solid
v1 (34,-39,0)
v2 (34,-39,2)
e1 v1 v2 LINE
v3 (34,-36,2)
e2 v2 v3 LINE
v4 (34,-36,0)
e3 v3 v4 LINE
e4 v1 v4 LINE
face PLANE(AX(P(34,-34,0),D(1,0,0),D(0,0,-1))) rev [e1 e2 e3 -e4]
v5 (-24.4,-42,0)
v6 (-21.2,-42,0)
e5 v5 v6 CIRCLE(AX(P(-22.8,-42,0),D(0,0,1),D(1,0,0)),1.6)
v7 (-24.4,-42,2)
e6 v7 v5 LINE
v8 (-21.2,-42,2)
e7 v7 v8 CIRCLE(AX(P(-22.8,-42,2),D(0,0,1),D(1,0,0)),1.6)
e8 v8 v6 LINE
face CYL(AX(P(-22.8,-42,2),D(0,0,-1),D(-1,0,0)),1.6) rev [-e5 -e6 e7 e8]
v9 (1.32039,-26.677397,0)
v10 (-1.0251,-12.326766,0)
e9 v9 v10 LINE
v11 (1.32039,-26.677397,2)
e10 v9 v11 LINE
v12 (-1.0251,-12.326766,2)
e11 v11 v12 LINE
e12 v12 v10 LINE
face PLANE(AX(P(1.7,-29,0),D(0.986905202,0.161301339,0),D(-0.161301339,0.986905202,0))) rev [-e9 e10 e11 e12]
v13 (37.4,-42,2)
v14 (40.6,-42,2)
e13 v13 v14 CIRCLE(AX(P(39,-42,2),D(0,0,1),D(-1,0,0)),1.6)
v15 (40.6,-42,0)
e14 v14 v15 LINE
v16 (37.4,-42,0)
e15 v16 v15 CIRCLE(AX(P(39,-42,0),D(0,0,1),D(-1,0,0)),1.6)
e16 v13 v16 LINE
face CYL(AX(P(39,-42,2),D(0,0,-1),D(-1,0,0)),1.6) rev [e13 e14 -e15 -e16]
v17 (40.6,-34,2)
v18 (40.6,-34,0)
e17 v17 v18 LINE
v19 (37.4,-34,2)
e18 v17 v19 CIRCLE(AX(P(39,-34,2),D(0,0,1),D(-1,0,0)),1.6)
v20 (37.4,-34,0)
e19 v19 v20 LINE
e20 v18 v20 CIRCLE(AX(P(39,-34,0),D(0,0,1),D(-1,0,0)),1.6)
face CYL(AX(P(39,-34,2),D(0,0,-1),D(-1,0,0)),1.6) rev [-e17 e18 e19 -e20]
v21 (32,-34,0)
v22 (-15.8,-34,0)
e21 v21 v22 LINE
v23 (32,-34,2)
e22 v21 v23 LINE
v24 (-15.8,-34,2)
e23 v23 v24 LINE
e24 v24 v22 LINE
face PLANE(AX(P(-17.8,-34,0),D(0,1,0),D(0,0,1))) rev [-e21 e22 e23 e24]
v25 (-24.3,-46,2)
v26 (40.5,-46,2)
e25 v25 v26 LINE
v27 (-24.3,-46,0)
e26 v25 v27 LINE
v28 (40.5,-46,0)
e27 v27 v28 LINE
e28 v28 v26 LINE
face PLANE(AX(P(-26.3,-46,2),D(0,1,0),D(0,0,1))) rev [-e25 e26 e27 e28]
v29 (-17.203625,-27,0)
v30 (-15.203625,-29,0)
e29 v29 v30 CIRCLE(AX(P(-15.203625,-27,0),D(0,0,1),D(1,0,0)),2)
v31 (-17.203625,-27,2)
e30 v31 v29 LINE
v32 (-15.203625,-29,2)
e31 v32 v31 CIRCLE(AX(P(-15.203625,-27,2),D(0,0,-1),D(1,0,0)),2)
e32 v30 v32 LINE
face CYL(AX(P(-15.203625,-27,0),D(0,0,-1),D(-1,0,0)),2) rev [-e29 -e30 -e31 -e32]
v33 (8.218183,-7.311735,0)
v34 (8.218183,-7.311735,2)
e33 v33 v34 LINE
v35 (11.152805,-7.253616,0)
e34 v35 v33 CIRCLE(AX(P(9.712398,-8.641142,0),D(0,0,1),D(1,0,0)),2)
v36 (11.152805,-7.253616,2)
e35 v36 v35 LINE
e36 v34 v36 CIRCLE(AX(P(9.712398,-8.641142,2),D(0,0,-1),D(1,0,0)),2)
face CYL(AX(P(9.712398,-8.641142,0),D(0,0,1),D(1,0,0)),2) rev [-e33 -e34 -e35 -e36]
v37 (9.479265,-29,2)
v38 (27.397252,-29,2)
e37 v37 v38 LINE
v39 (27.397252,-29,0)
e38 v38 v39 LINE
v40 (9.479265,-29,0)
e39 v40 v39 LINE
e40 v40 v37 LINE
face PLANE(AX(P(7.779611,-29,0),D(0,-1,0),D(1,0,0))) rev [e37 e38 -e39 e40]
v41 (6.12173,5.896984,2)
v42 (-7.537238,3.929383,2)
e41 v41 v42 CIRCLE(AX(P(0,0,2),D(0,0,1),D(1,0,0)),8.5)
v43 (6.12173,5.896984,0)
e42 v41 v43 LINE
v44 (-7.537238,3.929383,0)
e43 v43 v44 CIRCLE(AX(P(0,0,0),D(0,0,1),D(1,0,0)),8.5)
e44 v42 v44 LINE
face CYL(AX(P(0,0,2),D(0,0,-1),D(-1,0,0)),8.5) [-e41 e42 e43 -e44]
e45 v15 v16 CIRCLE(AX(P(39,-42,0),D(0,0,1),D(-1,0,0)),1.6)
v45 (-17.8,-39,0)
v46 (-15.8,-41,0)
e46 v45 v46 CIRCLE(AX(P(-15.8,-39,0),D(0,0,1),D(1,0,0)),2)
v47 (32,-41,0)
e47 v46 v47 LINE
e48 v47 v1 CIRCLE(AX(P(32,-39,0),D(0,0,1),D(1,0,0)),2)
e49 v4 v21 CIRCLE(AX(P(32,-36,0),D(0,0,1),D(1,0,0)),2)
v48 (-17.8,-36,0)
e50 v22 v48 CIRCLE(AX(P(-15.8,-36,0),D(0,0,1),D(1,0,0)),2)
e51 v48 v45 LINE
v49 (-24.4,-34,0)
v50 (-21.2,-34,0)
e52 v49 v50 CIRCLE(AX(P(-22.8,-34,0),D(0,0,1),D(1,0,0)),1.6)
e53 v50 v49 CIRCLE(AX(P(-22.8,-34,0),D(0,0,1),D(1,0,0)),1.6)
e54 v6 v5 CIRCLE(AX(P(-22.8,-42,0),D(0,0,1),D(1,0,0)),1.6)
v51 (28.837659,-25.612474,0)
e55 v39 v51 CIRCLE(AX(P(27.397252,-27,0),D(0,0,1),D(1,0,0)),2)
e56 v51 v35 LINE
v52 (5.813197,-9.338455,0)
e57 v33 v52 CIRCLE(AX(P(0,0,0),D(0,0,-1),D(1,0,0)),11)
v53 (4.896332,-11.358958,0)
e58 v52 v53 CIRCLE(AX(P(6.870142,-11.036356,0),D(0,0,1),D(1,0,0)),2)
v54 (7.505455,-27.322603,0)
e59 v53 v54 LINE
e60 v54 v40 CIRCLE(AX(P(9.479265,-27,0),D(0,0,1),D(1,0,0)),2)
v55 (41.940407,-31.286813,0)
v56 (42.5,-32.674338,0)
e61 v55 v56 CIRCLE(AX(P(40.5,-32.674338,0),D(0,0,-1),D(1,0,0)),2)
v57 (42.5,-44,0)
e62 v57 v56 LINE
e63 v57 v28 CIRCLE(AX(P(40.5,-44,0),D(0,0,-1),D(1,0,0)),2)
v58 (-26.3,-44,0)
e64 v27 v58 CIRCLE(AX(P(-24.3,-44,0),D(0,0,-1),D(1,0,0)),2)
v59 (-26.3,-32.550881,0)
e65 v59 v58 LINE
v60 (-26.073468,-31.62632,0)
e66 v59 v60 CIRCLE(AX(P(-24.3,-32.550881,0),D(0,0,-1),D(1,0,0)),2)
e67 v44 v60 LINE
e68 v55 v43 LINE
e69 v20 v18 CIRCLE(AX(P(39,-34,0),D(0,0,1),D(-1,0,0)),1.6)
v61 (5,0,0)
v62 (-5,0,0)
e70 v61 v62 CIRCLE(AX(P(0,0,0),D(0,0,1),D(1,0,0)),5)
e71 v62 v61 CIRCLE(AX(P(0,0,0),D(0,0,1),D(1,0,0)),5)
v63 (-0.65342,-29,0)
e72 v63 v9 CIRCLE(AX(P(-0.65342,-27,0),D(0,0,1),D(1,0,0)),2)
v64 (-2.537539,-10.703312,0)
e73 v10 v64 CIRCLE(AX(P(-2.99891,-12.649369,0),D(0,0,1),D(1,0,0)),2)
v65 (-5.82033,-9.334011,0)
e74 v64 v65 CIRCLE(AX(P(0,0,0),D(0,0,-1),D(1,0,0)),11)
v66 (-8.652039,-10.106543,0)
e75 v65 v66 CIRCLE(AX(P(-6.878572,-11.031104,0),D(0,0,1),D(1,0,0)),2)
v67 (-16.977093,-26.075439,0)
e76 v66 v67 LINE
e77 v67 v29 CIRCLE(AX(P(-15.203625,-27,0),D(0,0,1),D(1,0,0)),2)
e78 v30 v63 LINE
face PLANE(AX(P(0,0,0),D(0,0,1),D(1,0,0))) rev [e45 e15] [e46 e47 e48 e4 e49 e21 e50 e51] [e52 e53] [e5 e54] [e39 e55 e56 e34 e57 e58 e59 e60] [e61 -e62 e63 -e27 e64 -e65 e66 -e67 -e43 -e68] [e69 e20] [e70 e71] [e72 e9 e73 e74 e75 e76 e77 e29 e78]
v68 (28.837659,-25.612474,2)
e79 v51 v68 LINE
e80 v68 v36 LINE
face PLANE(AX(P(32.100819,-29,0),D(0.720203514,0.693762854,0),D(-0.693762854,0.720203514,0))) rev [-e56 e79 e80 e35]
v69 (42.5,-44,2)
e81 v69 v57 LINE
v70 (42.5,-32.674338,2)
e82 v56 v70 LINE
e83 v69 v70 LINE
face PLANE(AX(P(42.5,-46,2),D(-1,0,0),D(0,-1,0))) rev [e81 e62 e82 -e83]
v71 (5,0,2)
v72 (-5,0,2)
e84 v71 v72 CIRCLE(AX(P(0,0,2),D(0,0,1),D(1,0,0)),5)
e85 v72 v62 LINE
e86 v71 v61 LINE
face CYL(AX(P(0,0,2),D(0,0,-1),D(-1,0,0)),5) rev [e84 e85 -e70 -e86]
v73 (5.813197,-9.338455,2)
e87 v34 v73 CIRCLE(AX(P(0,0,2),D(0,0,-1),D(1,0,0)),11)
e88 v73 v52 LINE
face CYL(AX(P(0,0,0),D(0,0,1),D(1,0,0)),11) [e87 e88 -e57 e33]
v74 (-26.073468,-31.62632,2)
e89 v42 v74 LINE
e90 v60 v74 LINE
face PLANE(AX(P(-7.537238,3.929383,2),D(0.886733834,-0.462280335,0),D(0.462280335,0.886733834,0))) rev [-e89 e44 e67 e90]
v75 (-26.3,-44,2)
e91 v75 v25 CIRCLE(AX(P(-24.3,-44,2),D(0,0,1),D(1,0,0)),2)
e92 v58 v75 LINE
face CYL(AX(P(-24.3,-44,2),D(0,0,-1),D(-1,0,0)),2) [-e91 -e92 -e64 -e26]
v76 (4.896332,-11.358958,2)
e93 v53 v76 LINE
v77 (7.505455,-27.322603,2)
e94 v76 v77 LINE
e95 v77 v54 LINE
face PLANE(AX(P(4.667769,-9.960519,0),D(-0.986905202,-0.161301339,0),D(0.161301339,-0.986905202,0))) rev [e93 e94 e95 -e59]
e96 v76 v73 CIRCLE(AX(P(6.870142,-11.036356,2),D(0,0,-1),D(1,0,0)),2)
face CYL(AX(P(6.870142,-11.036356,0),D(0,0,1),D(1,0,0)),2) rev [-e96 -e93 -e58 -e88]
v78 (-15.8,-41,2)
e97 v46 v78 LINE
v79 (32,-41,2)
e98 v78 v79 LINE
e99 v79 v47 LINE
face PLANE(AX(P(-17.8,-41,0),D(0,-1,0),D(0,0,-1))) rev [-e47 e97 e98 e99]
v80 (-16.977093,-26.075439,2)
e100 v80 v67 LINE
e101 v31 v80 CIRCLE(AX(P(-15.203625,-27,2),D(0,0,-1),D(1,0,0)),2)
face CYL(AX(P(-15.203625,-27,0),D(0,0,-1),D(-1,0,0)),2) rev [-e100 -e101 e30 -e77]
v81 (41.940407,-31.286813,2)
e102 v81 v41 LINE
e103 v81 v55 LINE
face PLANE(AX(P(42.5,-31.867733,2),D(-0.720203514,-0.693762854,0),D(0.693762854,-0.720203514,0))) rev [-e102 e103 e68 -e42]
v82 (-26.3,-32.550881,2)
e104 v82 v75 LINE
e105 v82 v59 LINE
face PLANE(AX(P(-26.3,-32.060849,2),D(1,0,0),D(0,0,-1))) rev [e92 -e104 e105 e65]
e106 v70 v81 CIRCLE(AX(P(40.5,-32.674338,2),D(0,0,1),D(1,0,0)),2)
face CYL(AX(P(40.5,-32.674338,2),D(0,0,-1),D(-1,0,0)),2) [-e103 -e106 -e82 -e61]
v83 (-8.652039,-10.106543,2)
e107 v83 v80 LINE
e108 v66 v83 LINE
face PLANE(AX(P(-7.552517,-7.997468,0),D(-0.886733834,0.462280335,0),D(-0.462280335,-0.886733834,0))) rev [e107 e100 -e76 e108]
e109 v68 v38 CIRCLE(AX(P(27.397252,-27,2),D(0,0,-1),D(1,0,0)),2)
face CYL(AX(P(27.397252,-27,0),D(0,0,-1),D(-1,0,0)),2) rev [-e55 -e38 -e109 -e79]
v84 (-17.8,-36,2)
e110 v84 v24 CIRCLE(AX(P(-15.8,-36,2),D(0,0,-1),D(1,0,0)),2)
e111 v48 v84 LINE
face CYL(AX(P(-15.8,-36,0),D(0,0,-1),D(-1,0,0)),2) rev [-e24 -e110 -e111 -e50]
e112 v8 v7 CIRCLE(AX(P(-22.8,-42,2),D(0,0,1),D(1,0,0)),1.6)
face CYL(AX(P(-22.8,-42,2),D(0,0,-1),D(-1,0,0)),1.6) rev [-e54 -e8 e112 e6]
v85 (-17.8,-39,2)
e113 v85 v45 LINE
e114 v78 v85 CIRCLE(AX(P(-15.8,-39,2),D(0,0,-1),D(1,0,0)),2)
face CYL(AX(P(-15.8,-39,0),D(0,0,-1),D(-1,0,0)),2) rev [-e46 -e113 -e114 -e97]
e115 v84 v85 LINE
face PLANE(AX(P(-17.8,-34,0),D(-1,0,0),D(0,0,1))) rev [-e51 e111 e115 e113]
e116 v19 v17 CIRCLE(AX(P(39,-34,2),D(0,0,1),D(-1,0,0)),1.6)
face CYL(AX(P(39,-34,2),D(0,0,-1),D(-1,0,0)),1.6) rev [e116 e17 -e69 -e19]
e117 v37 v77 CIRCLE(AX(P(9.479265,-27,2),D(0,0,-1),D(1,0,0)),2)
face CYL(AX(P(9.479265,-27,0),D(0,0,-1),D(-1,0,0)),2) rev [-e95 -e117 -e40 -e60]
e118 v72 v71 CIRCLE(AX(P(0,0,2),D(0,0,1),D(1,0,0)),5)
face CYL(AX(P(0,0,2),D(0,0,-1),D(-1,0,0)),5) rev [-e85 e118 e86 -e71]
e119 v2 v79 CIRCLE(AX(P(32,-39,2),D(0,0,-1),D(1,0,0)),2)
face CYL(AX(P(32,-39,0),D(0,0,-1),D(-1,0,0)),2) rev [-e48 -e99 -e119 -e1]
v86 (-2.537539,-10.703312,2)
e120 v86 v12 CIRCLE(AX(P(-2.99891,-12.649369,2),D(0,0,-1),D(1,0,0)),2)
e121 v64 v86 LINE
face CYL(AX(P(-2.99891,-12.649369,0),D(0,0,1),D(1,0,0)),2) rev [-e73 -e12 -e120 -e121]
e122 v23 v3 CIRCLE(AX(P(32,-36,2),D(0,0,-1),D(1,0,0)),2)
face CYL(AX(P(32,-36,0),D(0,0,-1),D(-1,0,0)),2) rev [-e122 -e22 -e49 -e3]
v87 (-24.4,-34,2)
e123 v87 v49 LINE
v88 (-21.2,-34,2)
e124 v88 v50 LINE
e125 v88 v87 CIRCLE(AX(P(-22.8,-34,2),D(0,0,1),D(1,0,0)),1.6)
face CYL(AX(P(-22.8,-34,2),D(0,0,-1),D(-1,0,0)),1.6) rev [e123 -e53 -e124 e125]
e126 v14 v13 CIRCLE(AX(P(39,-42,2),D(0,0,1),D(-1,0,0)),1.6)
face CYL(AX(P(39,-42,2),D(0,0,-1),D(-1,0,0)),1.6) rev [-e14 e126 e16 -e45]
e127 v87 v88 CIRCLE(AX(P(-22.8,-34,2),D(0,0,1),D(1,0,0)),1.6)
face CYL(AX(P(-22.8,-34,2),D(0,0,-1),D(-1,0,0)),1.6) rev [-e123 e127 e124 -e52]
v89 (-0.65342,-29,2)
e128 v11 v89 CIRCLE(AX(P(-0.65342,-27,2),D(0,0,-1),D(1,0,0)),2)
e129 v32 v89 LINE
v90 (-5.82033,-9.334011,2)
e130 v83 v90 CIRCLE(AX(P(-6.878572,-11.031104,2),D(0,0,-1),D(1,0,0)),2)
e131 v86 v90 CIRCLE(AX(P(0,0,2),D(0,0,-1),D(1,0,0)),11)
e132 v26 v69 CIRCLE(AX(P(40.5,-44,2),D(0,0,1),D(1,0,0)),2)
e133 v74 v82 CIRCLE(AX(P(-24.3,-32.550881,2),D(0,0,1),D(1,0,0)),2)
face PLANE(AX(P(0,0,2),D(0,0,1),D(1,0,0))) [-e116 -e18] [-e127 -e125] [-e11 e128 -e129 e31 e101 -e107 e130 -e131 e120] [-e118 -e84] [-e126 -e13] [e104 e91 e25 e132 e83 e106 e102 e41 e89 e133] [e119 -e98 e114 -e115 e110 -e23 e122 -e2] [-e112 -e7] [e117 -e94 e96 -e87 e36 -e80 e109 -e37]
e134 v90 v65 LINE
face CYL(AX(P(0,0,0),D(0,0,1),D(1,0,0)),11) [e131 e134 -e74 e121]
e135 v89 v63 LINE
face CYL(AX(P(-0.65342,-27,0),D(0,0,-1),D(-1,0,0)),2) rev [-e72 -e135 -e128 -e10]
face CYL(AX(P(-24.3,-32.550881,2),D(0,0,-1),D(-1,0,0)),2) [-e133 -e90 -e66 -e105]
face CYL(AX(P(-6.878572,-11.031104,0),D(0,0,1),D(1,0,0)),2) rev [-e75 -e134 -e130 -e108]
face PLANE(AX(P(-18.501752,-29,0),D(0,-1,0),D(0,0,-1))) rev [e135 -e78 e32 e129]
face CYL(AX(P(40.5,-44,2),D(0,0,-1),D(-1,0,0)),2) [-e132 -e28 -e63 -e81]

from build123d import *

# Parameters (mm, degrees)
SKETCH_1_R          = 5
SKETCH_1_R_2        = 1.6
EXTRUDE_1_DEPTH     = 2
SKETCH_6_W          = 51.8
SKETCH_6_H          = 7
CUT_EXTRUDE_4_DEPTH = 63.659795723
FILLET_5_R          = 2
FILLET_6_R          = 2


with BuildPart() as part:
    # 草图1 → 凸台-拉伸1 (new body)
    with BuildSketch(Plane.XY):
        with BuildLine():
            Line((-26.3, -32.06084855), (-26.3, -46))
            Line((-26.3, -46), (42.5, -46))
            Line((42.5, -46), (42.5, -31.867732913))
            Line((42.5, -31.867732913), (6.12172987, 5.896984263))
            ThreePointArc((6.12172987, 5.896984263), (-1.211932074, 8.413157591), (-7.537237585, 3.929382851))
            Line((-7.537237585, 3.929382851), (-26.3, -32.06084855))
        make_face()
        Circle(SKETCH_1_R, mode=Mode.SUBTRACT)
        with Locations((-22.8, -34)):
            Circle(SKETCH_1_R_2, mode=Mode.SUBTRACT)
        with Locations((-22.8, -42)):
            Circle(SKETCH_1_R_2, mode=Mode.SUBTRACT)
        with Locations(Location((39, -42, 0), (0, 0, 180))):
            Circle(SKETCH_1_R_2, mode=Mode.SUBTRACT)
        with Locations(Location((39, -34, 0), (0, 0, 180))):
            Circle(SKETCH_1_R_2, mode=Mode.SUBTRACT)
    extrude(amount=EXTRUDE_1_DEPTH)

    # 草图6 → 切除-拉伸4 (cut, through all)
    with BuildSketch(Plane.XY.offset(2)):
        with BuildLine():
            Line((-7.552516715, -7.997467804), (-18.501752281, -29))
            Line((-18.501752281, -29), (1.7, -29))
            Line((1.7, -29), (-1.253662685, -10.928326948))
            ThreePointArc((-1.253662685, -10.928326948), (-4.640547676, -9.973230032), (-7.552516715, -7.997467804))
        make_face()
        with BuildLine():
            Line((4.667768527, -9.960518911), (7.779611281, -29))
            Line((7.779611281, -29), (32.100819179, -29))
            Line((32.100819179, -29), (9.502706469, -5.540629004))
            ThreePointArc((9.502706469, -5.540629004), (7.421889726, -8.118839381), (4.667768527, -9.960518911))
        make_face()
        with Locations((8.1, -37.5)):
            Rectangle(SKETCH_6_W, SKETCH_6_H)
    extrude(amount=-CUT_EXTRUDE_4_DEPTH, mode=Mode.SUBTRACT)

    # 圆角5
    fillet_5_edges = [part.edges().sort_by_distance(p)[0] for p in [
        (-17.8, -41, 1),
        (-17.8, -34, 1),
        (34, -34, 1),
        (34, -41, 1),
        (4.667768527, -9.960518911, 1),
        (9.502706469, -5.540629004, 1),
        (32.100819179, -29, 1),
        (7.779611281, -29, 1),
        (-7.552516715, -7.997467804, 1),
        (-1.253662685, -10.928326948, 1),
        (1.7, -29, 1),
        (-18.501752281, -29, 1),
    ]]
    fillet(fillet_5_edges, radius=FILLET_5_R)

    # 圆角6
    fillet_6_edges = [part.edges().sort_by_distance(p)[0] for p in [
        (42.5, -31.867732913, 1),
        (42.5, -46, 1),
        (-26.3, -46, 1),
        (-26.3, -32.06084855, 1),
    ]]
    fillet(fillet_6_edges, radius=FILLET_6_R)


solid = part.part
